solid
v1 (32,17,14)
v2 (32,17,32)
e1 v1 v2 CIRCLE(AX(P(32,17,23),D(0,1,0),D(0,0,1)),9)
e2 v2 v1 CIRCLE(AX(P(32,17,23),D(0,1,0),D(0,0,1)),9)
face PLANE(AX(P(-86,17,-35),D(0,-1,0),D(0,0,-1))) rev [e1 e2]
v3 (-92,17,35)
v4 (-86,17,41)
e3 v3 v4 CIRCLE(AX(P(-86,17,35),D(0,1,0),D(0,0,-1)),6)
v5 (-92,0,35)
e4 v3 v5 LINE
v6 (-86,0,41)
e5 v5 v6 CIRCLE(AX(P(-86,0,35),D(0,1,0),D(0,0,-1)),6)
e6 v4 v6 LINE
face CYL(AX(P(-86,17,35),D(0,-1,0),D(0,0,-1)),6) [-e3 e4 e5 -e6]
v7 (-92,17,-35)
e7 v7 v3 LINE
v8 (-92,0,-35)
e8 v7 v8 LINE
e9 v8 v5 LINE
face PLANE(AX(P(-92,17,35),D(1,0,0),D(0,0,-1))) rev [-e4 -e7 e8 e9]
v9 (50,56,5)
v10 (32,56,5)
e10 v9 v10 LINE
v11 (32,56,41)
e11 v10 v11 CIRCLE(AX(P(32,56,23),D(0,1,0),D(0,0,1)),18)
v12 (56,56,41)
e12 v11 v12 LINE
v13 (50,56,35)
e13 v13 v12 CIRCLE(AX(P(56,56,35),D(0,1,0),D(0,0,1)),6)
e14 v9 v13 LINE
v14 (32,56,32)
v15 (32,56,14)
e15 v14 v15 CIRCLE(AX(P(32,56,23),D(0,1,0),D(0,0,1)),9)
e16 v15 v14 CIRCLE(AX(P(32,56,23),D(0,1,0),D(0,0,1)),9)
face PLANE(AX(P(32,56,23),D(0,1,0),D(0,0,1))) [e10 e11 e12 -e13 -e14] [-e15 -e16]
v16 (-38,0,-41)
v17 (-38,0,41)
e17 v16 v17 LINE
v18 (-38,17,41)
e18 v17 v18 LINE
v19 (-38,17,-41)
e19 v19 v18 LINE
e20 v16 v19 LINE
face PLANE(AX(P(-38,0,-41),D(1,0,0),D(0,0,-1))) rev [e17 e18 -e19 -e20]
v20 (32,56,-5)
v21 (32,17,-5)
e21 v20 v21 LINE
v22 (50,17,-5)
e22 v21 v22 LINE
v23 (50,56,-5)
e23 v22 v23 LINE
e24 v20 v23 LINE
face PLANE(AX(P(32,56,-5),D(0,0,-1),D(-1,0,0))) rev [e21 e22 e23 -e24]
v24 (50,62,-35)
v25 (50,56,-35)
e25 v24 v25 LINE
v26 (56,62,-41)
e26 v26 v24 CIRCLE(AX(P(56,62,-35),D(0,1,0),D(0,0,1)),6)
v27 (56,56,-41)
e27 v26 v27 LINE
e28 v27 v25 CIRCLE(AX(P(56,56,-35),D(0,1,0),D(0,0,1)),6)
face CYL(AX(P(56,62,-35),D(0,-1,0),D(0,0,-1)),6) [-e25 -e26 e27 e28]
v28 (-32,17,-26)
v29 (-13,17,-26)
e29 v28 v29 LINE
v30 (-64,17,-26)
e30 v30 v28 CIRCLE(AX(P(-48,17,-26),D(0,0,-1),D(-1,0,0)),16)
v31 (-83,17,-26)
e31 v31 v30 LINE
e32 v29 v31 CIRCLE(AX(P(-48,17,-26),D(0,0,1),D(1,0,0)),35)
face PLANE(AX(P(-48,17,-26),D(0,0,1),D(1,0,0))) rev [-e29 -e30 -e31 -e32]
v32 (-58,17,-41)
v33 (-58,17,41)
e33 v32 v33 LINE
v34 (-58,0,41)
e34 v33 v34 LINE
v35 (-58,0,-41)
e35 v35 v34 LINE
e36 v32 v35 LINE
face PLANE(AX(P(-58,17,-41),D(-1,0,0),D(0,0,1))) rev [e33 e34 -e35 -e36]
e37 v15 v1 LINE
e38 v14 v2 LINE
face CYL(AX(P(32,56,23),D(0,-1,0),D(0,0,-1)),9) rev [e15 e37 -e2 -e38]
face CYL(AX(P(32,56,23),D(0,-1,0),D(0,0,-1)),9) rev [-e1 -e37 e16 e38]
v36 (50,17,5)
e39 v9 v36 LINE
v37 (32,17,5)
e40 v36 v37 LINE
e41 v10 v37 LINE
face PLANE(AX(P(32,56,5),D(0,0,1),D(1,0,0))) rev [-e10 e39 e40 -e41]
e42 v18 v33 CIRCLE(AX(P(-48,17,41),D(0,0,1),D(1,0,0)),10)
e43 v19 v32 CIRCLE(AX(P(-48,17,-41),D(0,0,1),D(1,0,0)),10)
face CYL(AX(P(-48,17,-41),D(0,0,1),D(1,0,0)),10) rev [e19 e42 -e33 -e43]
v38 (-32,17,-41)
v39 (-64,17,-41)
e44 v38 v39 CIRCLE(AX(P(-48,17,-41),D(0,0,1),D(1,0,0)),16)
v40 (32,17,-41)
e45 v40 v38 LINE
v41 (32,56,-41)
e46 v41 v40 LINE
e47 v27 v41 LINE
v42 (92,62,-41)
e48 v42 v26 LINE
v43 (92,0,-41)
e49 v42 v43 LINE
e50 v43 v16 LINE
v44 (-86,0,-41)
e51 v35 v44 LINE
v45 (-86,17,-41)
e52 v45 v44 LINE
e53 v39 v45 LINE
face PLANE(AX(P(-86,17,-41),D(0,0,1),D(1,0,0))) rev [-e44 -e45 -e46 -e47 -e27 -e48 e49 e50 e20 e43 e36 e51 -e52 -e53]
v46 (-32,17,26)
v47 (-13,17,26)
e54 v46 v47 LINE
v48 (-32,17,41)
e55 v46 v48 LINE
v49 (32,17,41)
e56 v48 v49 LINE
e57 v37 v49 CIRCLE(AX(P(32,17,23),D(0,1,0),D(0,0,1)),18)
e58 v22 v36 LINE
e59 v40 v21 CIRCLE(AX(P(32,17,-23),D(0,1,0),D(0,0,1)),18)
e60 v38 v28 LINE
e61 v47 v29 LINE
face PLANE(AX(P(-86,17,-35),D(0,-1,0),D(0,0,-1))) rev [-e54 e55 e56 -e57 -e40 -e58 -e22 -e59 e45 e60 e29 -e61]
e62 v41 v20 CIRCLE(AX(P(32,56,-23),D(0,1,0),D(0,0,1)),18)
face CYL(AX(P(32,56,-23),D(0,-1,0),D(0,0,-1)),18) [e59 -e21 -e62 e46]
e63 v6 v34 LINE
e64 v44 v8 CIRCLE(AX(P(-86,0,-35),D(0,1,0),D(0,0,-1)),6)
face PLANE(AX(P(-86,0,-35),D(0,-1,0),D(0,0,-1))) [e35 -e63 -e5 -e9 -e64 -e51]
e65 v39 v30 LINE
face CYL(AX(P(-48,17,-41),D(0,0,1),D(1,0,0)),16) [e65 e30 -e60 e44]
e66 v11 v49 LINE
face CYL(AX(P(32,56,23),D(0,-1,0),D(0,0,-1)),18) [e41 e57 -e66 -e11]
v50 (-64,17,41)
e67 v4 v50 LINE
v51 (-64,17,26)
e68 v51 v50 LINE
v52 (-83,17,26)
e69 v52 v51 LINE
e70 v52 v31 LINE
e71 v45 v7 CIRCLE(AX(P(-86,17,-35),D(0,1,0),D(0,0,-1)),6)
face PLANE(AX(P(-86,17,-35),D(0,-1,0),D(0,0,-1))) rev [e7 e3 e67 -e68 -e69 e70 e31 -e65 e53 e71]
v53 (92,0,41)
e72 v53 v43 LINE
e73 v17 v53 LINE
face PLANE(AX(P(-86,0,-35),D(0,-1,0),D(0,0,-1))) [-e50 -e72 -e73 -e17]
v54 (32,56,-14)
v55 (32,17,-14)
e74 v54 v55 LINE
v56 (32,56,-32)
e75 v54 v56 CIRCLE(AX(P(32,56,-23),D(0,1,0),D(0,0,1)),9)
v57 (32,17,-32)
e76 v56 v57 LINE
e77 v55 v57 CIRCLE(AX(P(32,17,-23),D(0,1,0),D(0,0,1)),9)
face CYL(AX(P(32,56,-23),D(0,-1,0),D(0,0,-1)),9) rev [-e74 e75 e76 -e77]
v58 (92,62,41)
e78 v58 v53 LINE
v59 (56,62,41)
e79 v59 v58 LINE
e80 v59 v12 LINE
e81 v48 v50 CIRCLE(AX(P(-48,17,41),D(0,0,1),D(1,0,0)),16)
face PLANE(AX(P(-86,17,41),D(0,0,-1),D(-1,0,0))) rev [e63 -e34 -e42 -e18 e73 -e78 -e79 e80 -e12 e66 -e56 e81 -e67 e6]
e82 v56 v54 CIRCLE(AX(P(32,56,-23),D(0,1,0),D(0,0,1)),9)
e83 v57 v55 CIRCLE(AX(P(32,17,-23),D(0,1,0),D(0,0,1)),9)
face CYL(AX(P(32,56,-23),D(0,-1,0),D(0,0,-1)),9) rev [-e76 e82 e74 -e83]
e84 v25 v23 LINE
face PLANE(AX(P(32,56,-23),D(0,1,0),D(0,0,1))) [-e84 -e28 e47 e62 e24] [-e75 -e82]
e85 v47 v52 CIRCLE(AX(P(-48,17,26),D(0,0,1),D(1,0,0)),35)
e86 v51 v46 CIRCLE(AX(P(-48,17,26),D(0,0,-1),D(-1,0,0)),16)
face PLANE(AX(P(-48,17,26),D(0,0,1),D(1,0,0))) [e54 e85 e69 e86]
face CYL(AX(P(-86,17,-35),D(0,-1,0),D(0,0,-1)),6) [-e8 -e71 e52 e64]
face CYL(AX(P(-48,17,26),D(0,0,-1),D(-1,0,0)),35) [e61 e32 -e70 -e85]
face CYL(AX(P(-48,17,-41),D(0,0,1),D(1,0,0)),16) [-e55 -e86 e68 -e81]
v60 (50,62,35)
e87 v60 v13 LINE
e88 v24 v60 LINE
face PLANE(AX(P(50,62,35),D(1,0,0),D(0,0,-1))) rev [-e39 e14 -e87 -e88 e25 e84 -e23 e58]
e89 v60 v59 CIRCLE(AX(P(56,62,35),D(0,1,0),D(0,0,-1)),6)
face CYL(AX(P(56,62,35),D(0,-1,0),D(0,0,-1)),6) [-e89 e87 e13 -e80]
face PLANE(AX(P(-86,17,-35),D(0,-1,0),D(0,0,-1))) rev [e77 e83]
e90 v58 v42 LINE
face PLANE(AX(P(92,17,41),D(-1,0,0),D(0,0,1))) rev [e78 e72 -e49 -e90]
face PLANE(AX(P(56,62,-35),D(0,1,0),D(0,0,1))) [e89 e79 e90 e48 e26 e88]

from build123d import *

# Parameters (mm, degrees)
BASE_PLATE_184X82X17_DEPTH      = 17
BEARING_SADDLE_DEPTH            = 45
RAISED_PAD_DEPTH                = 82
STEP_PROFILE_DEPTH              = 82
SLOT_CUT_DEPTH                  = 82
BOLT_BOSSES_SKETCH_R            = 9
BOLT_BOSSES_2X_WITH_HOLES_DEPTH = 39
END_BLOCK_DEPTH                 = 26


with BuildPart() as part:
    # Base Plate Sketch → Base Plate 184x82x17 (new body)
    with BuildSketch(Plane(origin=(0, 0, 0), x_dir=(1, 0, 0), z_dir=(0, 1, 0))):
        with BuildLine():
            Line((-86, -41), (92, -41))
            Line((92, -41), (92, 41))
            Line((92, 41), (-86, 41))
            ThreePointArc((-86, 41), (-90.242640687, 39.242640687), (-92, 35))
            Line((-92, 35), (-92, -35))
            ThreePointArc((-92, -35), (-90.242640687, -39.242640687), (-86, -41))
        make_face()
    extrude(amount=BASE_PLATE_184X82X17_DEPTH)

    # Bearing Saddle Sketch → Bearing Saddle (add)
    with BuildSketch(Plane(origin=(0, 17, 0), x_dir=(1, 0, 0), z_dir=(0, 1, 0))):
        with BuildLine():
            Line((92, -41), (56, -41))
            ThreePointArc((56, -41), (51.757359313, -39.242640687), (50, -35))
            Line((50, -35), (50, 35))
            ThreePointArc((50, 35), (51.757359313, 39.242640687), (56, 41))
            Line((56, 41), (92, 41))
            Line((92, 41), (92, -41))
        make_face()
    extrude(amount=BEARING_SADDLE_DEPTH)

    # Raised Pad Sketch → Raised Pad (add)
    with BuildSketch(Plane.XY.offset(41)):
        with BuildLine():
            Line((-58, 17), (-58, 0))
            Line((-58, 0), (-38, 0))
            Line((-38, 0), (-38, 17))
            ThreePointArc((-38, 17), (-48, 27), (-58, 17))
        make_face()
    extrude(amount=-RAISED_PAD_DEPTH)

    # Step Profile Sketch → Step Profile (add)
    with BuildSketch(Plane.XY.offset(41)):
        with BuildLine():
            Line((-64, 17), (-58, 17))
            ThreePointArc((-58, 17), (-48, 27), (-38, 17))
            Line((-38, 17), (-32, 17))
            ThreePointArc((-32, 17), (-48, 33), (-64, 17))
        make_face()
    extrude(amount=-STEP_PROFILE_DEPTH)

    # Slot Cut Sketch → Slot Cut (cut)
    with BuildSketch(Plane.XY.offset(41)):
        with BuildLine():
            Line((-58, 17), (-58, 0))
            Line((-58, 0), (-38, 0))
            Line((-38, 0), (-38, 17))
            ThreePointArc((-38, 17), (-48, 27), (-58, 17))
        make_face()
    extrude(amount=-SLOT_CUT_DEPTH, mode=Mode.SUBTRACT)

    # Bolt Bosses Sketch → Bolt Bosses 2x with Holes (add)
    # profile 1 of 2: a face of its own
    with BuildSketch(Plane(origin=(0, 17, 0), x_dir=(1, 0, 0), z_dir=(0, 1, 0))):
        with BuildLine():
            Line((32, 41), (56, 41))
            Line((56, 41), (56, 5))
            Line((56, 5), (32, 5))
            ThreePointArc((32, 5), (14, 23), (32, 41))
        make_face()
        with Locations(Location((32, 23, 0), (0, 0, 270))):
            Circle(BOLT_BOSSES_SKETCH_R, mode=Mode.SUBTRACT)
    # profile 2 of 2: a face of its own
    with BuildSketch(Plane(origin=(0, 17, 0), x_dir=(1, 0, 0), z_dir=(0, 1, 0))):
        with BuildLine():
            Line((32, -5), (56, -5))
            Line((56, -5), (56, -41))
            Line((56, -41), (32, -41))
            ThreePointArc((32, -41), (14, -23), (32, -5))
        make_face()
        with Locations(Location((32, -23, 0), (0, 0, 270))):
            Circle(BOLT_BOSSES_SKETCH_R, mode=Mode.SUBTRACT)
    extrude(amount=BOLT_BOSSES_2X_WITH_HOLES_DEPTH)

    # End Block Sketch → End Block (add, symmetric)
    with BuildSketch(Plane.XY):
        with BuildLine():
            Line((-83, 17), (-64, 17))
            ThreePointArc((-64, 17), (-48, 33), (-32, 17))
            Line((-32, 17), (-13, 17))
            ThreePointArc((-13, 17), (-48, 52), (-83, 17))
        make_face()
    extrude(amount=END_BLOCK_DEPTH, both=True)


solid = part.part
